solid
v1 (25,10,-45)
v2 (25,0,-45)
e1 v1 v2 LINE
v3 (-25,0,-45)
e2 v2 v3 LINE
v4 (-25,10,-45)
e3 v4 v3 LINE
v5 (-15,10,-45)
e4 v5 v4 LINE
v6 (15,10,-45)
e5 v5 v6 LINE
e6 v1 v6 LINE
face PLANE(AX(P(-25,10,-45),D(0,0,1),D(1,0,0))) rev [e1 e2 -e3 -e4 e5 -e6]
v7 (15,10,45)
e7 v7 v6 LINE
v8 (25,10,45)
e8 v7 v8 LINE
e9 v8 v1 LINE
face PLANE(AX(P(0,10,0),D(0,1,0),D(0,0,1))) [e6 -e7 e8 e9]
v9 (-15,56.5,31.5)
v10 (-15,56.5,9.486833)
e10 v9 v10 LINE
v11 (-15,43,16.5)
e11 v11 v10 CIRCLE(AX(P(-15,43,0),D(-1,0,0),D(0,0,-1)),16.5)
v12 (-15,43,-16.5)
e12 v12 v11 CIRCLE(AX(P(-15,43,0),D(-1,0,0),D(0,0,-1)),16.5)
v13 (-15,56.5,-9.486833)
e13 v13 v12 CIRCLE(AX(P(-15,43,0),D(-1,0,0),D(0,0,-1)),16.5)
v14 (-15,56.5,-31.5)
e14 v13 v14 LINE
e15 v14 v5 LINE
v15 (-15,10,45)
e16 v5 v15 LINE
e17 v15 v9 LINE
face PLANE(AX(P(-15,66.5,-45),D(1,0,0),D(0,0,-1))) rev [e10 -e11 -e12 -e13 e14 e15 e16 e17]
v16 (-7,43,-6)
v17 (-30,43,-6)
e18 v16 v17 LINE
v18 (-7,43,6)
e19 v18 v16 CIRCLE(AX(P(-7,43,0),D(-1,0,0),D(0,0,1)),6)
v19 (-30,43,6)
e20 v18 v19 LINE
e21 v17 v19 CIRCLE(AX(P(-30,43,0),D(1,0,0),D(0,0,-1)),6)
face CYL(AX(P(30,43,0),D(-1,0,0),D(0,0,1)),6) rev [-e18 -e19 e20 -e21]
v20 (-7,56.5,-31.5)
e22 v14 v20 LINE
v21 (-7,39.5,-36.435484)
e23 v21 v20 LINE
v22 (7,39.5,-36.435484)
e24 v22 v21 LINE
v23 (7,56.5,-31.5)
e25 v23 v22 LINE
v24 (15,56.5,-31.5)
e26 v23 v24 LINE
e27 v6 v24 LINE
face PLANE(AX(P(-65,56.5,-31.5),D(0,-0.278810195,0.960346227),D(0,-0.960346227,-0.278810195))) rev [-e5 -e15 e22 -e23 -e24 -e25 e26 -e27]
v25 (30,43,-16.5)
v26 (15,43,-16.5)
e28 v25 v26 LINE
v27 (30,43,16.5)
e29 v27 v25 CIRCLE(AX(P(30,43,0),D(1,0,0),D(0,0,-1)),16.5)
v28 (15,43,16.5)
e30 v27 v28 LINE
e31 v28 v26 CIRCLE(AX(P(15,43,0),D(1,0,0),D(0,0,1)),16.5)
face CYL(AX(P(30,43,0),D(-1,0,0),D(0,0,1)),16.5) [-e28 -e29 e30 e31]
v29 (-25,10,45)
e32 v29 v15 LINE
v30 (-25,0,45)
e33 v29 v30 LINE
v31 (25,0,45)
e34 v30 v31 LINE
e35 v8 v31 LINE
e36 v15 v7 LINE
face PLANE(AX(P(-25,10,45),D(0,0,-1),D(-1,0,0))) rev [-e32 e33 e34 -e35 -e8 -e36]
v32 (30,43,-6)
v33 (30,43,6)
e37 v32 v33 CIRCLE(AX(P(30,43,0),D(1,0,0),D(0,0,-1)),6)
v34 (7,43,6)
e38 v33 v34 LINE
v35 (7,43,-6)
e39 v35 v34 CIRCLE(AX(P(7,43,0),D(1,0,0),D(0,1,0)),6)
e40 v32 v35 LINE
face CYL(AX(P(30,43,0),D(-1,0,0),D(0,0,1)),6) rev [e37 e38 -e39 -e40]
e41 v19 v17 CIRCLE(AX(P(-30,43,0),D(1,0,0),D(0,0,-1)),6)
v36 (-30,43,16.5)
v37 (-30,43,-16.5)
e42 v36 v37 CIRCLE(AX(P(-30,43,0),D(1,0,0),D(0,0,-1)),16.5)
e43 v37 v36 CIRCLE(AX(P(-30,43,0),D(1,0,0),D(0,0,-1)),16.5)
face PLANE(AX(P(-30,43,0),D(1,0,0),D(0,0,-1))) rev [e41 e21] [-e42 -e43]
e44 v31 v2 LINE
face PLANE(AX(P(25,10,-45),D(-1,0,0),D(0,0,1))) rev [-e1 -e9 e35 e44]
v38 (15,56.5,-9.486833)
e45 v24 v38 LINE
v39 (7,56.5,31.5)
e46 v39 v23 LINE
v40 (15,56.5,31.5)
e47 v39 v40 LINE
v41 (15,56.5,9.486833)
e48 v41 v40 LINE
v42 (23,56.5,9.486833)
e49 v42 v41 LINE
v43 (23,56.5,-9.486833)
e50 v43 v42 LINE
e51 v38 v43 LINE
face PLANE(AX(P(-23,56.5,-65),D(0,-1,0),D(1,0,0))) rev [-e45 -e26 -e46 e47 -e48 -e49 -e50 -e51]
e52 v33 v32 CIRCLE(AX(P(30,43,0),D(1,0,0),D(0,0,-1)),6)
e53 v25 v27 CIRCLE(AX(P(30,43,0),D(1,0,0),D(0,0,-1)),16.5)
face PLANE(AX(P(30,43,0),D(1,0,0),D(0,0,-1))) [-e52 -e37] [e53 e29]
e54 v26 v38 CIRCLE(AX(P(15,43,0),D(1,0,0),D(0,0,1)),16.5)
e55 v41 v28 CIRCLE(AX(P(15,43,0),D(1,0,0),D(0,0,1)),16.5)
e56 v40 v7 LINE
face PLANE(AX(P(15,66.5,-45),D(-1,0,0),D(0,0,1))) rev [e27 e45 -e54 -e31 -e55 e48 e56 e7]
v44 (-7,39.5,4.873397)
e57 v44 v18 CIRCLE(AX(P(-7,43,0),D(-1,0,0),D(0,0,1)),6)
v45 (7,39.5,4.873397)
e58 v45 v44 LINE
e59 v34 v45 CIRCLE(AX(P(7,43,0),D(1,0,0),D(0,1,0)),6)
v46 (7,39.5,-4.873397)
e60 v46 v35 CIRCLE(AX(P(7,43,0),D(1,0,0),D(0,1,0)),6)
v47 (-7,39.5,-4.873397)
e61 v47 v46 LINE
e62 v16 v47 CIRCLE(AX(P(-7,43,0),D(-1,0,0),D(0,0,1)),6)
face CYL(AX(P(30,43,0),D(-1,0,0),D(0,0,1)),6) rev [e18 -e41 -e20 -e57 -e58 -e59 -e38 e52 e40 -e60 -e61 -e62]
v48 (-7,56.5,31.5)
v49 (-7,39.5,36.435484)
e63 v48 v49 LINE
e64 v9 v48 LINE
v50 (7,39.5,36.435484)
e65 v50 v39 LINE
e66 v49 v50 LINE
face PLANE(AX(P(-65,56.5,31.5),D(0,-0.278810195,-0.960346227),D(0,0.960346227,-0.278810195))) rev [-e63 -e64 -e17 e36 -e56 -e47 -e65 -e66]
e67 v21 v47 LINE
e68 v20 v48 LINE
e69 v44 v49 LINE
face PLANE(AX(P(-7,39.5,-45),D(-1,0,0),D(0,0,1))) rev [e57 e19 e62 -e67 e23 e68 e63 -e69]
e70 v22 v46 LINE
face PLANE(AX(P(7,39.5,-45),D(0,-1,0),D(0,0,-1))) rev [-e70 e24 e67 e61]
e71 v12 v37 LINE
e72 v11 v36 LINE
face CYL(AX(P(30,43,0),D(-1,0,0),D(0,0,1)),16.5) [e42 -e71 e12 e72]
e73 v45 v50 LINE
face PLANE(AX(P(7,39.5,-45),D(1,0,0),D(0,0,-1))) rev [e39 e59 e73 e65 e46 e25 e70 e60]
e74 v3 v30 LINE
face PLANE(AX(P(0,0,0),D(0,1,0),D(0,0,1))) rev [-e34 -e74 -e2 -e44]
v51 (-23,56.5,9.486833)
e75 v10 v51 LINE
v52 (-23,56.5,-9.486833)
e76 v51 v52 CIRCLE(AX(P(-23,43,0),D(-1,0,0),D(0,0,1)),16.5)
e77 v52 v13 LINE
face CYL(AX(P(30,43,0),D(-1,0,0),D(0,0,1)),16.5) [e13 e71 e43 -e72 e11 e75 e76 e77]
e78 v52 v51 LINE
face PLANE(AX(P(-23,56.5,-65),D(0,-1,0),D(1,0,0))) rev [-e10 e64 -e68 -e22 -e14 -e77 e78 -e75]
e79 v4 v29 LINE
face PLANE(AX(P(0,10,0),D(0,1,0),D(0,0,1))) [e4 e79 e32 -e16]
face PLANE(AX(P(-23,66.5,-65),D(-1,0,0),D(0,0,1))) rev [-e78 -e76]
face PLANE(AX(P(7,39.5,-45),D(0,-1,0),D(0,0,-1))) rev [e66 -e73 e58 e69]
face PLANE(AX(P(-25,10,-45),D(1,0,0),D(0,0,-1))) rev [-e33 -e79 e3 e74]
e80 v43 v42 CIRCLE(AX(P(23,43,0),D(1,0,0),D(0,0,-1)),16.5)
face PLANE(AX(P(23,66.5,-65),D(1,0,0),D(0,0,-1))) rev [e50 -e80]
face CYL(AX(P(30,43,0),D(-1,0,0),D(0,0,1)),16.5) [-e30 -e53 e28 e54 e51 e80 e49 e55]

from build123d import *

# Parameters (mm, degrees)
BASE_PLATE_SKETCH_W        = 50
BASE_PLATE_SKETCH_H        = 90
BASE_PLATE_90X50X10_DEPTH  = 10
UPRIGHT_PROFILE_SKETCH_W   = 30
UPRIGHT_PROFILE_SKETCH_H   = 90
TAPERED_UPRIGHT_DEPTH      = 56.5
UPRIGHT_TRIM_SKETCH_W      = 14
UPRIGHT_TRIM_SKETCH_H      = 27
UPRIGHT_TRIM_CUT_DEPTH     = 115.661458215
BEARING_BOSS_SKETCH_R      = 16.5
BEARING_BOSS_SKETCH_R_2    = 6
BEARING_BOSS_DEPTH         = 30
CENTRE_SLOT_SKETCH_W       = 46
CENTRE_SLOT_SKETCH_H       = 10
CENTRE_SLOT_CUT_DEPTH      = 65
TOP_SLOT_CUT_DEPTH         = 65
BEARING_BORE_SKETCH_R      = 6
BEARING_BORE_THROUGH_DEPTH = 65
BOSS_NOTCH_SKETCH_W        = 14
BOSS_NOTCH_SKETCH_H        = 17
BOSS_NOTCH_CUT_DEPTH       = 65


with BuildPart() as part:
    # Base Plate Sketch → Base Plate 90x50x10 (new body)
    with BuildSketch(Plane(origin=(0, 0, 0), x_dir=(1, 0, 0), z_dir=(0, 1, 0))):
        Rectangle(BASE_PLATE_SKETCH_W, BASE_PLATE_SKETCH_H)
    extrude(amount=BASE_PLATE_90X50X10_DEPTH)

    # Upright Profile Sketch → Tapered Upright (add)
    with BuildSketch(Plane(origin=(0, 10, 0), x_dir=(1, 0, 0), z_dir=(0, 1, 0))):
        Rectangle(UPRIGHT_PROFILE_SKETCH_W, UPRIGHT_PROFILE_SKETCH_H)
    extrude(amount=TAPERED_UPRIGHT_DEPTH)

    # Upright Trim Sketch → Upright Trim Cut (cut, through all)
    with BuildSketch(Plane.XY.offset(45)):
        with Locations((0, 53)):
            Rectangle(UPRIGHT_TRIM_SKETCH_W, UPRIGHT_TRIM_SKETCH_H)
    extrude(amount=-UPRIGHT_TRIM_CUT_DEPTH, mode=Mode.SUBTRACT)

    # Bearing Boss Sketch → Bearing Boss (add, symmetric)
    with BuildSketch(Plane(origin=(0, 0, 0), x_dir=(0, 0, -1), z_dir=(1, 0, 0))):
        with Locations((0, 43)):
            Circle(BEARING_BOSS_SKETCH_R)
        with Locations((0, 43)):
            Circle(BEARING_BOSS_SKETCH_R_2, mode=Mode.SUBTRACT)
    extrude(amount=BEARING_BOSS_DEPTH, both=True)

    # Centre Slot Sketch → Centre Slot Cut (cut, symmetric)
    with BuildSketch(Plane.XY):
        with Locations((0, 61.5)):
            Rectangle(CENTRE_SLOT_SKETCH_W, CENTRE_SLOT_SKETCH_H)
    extrude(amount=CENTRE_SLOT_CUT_DEPTH, both=True, mode=Mode.SUBTRACT)

    # Top Slot Sketch → Top Slot Cut (cut, symmetric)
    with BuildSketch(Plane(origin=(0, 0, 0), x_dir=(0, 0, -1), z_dir=(1, 0, 0))):
        Polygon((-31.5, 56.5), (-45, 10), (-45, 56.5), align=None)
        Polygon((31.5, 56.5), (45, 10), (45, 56.5), align=None)
    extrude(amount=TOP_SLOT_CUT_DEPTH, both=True, mode=Mode.SUBTRACT)

    # Bearing Bore Sketch → Bearing Bore Through (cut, symmetric)
    with BuildSketch(Plane.ZY.offset(15)):
        with Locations(Location((0, 43, 0), (0, 0, 180))):
            Circle(BEARING_BORE_SKETCH_R)
    extrude(amount=BEARING_BORE_THROUGH_DEPTH, both=True, mode=Mode.SUBTRACT)

    # Boss Notch Sketch → Boss Notch Cut (cut, symmetric)
    with BuildSketch(Plane.XY):
        with Locations((0, 48)):
            Rectangle(BOSS_NOTCH_SKETCH_W, BOSS_NOTCH_SKETCH_H)
    extrude(amount=BOSS_NOTCH_CUT_DEPTH, both=True, mode=Mode.SUBTRACT)


solid = part.part
